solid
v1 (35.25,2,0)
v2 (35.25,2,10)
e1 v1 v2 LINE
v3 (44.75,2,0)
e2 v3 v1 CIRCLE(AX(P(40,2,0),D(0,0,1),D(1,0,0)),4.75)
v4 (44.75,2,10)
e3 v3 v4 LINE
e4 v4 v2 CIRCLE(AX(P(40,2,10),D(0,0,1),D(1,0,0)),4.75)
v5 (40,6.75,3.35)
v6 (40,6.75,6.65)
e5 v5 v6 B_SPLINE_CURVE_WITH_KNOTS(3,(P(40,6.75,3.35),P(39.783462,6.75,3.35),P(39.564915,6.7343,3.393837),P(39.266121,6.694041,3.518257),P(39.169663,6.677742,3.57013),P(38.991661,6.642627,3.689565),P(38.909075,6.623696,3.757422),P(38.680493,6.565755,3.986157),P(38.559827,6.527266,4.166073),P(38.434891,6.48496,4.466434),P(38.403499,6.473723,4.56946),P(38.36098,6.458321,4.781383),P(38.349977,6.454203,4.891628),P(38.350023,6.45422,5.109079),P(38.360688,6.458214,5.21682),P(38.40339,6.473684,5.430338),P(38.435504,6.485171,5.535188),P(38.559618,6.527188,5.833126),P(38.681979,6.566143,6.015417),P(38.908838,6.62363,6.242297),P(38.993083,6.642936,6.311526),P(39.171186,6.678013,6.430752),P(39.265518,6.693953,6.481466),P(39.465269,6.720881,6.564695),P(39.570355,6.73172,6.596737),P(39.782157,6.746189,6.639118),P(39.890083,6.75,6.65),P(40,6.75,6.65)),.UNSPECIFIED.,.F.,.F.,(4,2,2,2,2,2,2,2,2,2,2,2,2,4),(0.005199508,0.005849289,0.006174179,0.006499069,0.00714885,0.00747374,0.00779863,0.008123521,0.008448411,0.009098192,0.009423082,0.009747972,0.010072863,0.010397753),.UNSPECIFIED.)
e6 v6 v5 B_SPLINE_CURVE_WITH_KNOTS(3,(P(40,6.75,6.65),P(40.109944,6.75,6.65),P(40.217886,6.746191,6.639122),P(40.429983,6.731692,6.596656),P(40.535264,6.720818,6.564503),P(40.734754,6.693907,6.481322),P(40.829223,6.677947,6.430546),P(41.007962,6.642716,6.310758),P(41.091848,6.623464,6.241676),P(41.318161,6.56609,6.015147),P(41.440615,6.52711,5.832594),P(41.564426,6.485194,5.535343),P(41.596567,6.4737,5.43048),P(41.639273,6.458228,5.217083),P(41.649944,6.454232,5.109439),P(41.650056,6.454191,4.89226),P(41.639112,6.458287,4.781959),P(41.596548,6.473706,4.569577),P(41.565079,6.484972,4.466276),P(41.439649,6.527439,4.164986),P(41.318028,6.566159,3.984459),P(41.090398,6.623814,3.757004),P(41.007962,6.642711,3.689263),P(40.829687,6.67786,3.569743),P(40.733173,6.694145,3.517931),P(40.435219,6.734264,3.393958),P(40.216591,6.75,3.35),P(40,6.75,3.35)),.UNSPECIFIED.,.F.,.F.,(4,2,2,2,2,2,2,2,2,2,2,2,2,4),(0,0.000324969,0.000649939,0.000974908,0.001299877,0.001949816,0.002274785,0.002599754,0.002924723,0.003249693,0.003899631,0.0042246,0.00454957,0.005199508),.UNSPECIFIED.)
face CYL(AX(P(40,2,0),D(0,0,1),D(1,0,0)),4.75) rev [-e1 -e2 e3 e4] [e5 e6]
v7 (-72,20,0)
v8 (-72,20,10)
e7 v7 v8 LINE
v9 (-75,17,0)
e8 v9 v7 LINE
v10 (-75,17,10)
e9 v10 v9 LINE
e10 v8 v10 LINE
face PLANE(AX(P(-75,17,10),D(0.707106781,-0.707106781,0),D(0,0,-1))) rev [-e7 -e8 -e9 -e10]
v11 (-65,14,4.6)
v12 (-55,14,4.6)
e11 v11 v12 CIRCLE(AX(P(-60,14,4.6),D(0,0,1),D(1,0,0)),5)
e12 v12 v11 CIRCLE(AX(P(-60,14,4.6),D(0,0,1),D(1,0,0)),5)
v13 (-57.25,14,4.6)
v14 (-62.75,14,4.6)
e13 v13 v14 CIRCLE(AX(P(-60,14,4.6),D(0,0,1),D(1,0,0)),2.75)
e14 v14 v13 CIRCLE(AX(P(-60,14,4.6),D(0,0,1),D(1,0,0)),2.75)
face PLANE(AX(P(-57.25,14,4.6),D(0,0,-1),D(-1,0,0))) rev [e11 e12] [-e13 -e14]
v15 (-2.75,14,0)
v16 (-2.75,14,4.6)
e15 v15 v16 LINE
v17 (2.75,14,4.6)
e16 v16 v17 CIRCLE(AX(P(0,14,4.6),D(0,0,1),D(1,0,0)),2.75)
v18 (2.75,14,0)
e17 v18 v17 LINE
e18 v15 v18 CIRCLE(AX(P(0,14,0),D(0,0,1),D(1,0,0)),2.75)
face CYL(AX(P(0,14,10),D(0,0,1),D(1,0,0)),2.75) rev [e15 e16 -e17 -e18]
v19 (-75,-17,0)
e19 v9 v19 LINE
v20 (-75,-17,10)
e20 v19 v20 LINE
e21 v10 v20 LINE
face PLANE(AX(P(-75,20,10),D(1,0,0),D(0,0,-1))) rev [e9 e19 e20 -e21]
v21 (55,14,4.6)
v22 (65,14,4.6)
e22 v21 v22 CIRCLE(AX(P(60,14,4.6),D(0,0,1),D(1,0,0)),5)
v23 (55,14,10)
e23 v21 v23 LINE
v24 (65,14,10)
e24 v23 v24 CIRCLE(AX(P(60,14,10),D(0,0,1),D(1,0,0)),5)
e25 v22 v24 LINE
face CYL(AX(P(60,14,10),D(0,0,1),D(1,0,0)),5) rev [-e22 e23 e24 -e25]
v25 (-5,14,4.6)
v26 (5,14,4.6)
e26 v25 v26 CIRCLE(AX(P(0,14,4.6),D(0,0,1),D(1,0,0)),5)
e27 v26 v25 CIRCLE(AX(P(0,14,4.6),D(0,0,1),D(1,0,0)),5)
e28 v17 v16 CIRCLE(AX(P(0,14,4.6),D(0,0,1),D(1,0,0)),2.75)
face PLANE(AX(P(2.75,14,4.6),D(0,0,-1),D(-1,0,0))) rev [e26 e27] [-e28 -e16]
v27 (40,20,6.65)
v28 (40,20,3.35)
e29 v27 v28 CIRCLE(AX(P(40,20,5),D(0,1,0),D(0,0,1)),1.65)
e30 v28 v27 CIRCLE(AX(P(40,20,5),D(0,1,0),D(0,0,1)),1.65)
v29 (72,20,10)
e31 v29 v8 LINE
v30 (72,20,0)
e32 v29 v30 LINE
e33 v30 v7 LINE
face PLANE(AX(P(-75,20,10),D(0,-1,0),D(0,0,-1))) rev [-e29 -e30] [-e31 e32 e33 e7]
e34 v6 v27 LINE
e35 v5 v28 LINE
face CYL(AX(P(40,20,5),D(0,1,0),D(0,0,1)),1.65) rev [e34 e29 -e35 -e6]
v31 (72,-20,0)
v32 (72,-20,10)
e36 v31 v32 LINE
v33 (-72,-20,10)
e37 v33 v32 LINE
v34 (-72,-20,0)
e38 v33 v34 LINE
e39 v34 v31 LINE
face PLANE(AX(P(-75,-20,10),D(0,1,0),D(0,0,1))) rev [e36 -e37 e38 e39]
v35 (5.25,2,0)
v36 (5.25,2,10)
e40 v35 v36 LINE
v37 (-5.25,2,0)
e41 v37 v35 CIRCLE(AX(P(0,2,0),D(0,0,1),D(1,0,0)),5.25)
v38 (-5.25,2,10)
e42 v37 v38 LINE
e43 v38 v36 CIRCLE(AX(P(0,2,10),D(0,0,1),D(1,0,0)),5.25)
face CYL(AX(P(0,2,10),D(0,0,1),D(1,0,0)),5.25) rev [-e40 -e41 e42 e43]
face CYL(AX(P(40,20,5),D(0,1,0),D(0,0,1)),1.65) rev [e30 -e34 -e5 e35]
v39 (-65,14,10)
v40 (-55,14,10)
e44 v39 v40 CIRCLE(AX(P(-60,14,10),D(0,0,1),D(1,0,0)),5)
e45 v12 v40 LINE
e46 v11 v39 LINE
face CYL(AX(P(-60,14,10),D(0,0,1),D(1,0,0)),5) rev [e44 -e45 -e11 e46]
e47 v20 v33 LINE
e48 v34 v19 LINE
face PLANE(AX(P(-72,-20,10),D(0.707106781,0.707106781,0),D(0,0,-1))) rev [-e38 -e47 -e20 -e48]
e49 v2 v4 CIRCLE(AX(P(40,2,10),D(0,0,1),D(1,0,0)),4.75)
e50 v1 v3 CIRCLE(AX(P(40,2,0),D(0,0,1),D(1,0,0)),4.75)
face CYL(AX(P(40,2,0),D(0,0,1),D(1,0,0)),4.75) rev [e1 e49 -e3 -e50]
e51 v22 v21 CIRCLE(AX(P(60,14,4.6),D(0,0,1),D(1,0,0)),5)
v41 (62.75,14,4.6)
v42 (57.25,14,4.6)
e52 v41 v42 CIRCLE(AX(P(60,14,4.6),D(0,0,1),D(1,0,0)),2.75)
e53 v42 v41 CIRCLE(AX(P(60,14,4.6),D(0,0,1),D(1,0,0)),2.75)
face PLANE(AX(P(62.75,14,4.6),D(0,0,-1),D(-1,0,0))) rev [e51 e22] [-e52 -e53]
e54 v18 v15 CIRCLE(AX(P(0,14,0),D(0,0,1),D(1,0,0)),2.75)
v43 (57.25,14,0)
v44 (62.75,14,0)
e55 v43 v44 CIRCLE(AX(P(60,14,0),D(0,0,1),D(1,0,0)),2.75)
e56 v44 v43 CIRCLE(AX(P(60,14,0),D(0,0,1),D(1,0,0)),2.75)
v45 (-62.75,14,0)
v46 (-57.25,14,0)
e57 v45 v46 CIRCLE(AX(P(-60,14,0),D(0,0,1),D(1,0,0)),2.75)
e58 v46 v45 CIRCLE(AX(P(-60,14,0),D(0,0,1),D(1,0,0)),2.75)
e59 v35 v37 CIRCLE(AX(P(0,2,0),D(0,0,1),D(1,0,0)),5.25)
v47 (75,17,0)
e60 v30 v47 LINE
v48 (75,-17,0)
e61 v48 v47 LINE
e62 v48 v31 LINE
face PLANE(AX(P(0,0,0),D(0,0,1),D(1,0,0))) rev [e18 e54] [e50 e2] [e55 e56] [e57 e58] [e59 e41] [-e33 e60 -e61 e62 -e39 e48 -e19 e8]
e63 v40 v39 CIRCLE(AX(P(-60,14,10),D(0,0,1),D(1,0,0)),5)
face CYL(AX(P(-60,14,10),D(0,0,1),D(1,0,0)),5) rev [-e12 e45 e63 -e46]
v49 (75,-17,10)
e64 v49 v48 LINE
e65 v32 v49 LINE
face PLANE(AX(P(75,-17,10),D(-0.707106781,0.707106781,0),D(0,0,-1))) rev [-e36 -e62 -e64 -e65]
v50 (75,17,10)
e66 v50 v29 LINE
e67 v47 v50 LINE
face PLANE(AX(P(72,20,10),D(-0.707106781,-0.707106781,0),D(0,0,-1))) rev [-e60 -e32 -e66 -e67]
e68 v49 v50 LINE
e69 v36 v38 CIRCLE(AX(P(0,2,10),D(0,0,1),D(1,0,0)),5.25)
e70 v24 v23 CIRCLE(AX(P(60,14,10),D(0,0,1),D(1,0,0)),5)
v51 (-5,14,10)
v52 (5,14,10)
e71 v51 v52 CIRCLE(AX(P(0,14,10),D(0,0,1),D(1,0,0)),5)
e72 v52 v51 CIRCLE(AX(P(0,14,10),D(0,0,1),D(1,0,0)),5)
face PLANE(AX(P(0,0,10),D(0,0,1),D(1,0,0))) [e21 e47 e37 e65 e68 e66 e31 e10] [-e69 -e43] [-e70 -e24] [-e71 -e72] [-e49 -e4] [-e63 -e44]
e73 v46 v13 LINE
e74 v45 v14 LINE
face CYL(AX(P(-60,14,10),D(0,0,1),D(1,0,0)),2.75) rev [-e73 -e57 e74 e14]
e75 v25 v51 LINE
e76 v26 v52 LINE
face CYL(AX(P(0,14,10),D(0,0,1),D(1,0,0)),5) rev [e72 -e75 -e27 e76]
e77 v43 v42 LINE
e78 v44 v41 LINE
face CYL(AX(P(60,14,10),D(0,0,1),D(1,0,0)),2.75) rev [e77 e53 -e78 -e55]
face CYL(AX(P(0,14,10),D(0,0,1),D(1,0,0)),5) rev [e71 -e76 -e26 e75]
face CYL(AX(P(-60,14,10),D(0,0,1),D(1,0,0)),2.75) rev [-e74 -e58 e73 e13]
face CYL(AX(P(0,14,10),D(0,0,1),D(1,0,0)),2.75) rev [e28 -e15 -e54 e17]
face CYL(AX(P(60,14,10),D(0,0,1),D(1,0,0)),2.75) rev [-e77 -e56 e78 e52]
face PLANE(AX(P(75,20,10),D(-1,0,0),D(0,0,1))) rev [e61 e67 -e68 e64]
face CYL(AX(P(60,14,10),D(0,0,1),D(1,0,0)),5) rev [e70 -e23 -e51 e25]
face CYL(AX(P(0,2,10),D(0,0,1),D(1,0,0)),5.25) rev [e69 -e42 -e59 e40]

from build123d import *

# Parameters (mm, degrees)
SKETCH1_W                                           = 150
SKETCH1_H                                           = 40
BOSS_EXTRUDE1_DEPTH                                 = 10
SKETCH2_R                                           = 4.75
CUT_EXTRUDE1_DEPTH                                  = 79.262379212
F_10_5_10_5_DIAMETER_HOLE1_D                        = 10.5
F_10_5_10_5_DIAMETER_HOLE1_DEPTH                    = 76
F_10_5_10_5_DIAMETER_HOLE1_TIP                      = 3.15451825
CBORE_FOR_M5_HEX_SOCKET_HEAD_CAP_SCREW1_D           = 5.5
CBORE_FOR_M5_HEX_SOCKET_HEAD_CAP_SCREW1_CBORE_D     = 10
CBORE_FOR_M5_HEX_SOCKET_HEAD_CAP_SCREW1_CBORE_DEPTH = 5.4
M4_TAPPED_HOLE1_REACH                               = 87.586
M4_TAPPED_HOLE1_BORE_R                              = 1.65
CHAMFER1_SIZE                                       = 3


with BuildPart() as part:
    # Sketch1 → Boss-Extrude1 (new body)
    with BuildSketch(Plane.XY):
        Rectangle(SKETCH1_W, SKETCH1_H)
    extrude(amount=BOSS_EXTRUDE1_DEPTH)

    # Sketch2 → Cut-Extrude1 (cut, through all)
    with BuildSketch(Plane.XY.offset(10)):
        with Locations((40, 2)):
            Circle(SKETCH2_R)
    extrude(amount=-CUT_EXTRUDE1_DEPTH, mode=Mode.SUBTRACT)

    # Ø10.5 (10.5) Diameter Hole1
    with Locations(Plane.XY.offset(10)):
        with Locations((0, 2)):
            Hole(F_10_5_10_5_DIAMETER_HOLE1_D / 2, depth=F_10_5_10_5_DIAMETER_HOLE1_DEPTH)
            with Locations((0, 0, -(F_10_5_10_5_DIAMETER_HOLE1_DEPTH + F_10_5_10_5_DIAMETER_HOLE1_TIP / 2))):  # 118° drill point
                Cone(0, F_10_5_10_5_DIAMETER_HOLE1_D / 2, F_10_5_10_5_DIAMETER_HOLE1_TIP, mode=Mode.SUBTRACT)

    # CBORE for M5 Hex Socket Head Cap Screw1 (through all)
    with Locations(Plane.XY.offset(10)):
        with Locations((60, 14), (0, 14), (-60, 14)):
            CounterBoreHole(CBORE_FOR_M5_HEX_SOCKET_HEAD_CAP_SCREW1_D / 2, CBORE_FOR_M5_HEX_SOCKET_HEAD_CAP_SCREW1_CBORE_D / 2, CBORE_FOR_M5_HEX_SOCKET_HEAD_CAP_SCREW1_CBORE_DEPTH)

    # M4 Tapped Hole1 bore → M4 Tapped Hole1 (cut, up to next)
    with BuildSketch(Plane(origin=(0, 20, 0), x_dir=(1, 0, 0), z_dir=(0, 1, 0)), mode=Mode.PRIVATE) as m4_tapped_hole1_sk1:
        with Locations((40, -5)):
            Circle(M4_TAPPED_HOLE1_BORE_R)
    m4_tapped_hole1_tool1 = extrude(m4_tapped_hole1_sk1.sketch, amount=-M4_TAPPED_HOLE1_REACH, mode=Mode.PRIVATE) & part.part
    add(m4_tapped_hole1_tool1.solids().sort_by_distance((40, 20, 5))[0], mode=Mode.SUBTRACT)

    # Chamfer1
    chamfer1_edges = [part.edges().sort_by_distance(p)[0] for p in [
        (75, -20, 5),
        (-75, -20, 5),
        (-75, 20, 5),
        (75, 20, 5),
    ]]
    chamfer(chamfer1_edges, length=CHAMFER1_SIZE)


solid = part.part
